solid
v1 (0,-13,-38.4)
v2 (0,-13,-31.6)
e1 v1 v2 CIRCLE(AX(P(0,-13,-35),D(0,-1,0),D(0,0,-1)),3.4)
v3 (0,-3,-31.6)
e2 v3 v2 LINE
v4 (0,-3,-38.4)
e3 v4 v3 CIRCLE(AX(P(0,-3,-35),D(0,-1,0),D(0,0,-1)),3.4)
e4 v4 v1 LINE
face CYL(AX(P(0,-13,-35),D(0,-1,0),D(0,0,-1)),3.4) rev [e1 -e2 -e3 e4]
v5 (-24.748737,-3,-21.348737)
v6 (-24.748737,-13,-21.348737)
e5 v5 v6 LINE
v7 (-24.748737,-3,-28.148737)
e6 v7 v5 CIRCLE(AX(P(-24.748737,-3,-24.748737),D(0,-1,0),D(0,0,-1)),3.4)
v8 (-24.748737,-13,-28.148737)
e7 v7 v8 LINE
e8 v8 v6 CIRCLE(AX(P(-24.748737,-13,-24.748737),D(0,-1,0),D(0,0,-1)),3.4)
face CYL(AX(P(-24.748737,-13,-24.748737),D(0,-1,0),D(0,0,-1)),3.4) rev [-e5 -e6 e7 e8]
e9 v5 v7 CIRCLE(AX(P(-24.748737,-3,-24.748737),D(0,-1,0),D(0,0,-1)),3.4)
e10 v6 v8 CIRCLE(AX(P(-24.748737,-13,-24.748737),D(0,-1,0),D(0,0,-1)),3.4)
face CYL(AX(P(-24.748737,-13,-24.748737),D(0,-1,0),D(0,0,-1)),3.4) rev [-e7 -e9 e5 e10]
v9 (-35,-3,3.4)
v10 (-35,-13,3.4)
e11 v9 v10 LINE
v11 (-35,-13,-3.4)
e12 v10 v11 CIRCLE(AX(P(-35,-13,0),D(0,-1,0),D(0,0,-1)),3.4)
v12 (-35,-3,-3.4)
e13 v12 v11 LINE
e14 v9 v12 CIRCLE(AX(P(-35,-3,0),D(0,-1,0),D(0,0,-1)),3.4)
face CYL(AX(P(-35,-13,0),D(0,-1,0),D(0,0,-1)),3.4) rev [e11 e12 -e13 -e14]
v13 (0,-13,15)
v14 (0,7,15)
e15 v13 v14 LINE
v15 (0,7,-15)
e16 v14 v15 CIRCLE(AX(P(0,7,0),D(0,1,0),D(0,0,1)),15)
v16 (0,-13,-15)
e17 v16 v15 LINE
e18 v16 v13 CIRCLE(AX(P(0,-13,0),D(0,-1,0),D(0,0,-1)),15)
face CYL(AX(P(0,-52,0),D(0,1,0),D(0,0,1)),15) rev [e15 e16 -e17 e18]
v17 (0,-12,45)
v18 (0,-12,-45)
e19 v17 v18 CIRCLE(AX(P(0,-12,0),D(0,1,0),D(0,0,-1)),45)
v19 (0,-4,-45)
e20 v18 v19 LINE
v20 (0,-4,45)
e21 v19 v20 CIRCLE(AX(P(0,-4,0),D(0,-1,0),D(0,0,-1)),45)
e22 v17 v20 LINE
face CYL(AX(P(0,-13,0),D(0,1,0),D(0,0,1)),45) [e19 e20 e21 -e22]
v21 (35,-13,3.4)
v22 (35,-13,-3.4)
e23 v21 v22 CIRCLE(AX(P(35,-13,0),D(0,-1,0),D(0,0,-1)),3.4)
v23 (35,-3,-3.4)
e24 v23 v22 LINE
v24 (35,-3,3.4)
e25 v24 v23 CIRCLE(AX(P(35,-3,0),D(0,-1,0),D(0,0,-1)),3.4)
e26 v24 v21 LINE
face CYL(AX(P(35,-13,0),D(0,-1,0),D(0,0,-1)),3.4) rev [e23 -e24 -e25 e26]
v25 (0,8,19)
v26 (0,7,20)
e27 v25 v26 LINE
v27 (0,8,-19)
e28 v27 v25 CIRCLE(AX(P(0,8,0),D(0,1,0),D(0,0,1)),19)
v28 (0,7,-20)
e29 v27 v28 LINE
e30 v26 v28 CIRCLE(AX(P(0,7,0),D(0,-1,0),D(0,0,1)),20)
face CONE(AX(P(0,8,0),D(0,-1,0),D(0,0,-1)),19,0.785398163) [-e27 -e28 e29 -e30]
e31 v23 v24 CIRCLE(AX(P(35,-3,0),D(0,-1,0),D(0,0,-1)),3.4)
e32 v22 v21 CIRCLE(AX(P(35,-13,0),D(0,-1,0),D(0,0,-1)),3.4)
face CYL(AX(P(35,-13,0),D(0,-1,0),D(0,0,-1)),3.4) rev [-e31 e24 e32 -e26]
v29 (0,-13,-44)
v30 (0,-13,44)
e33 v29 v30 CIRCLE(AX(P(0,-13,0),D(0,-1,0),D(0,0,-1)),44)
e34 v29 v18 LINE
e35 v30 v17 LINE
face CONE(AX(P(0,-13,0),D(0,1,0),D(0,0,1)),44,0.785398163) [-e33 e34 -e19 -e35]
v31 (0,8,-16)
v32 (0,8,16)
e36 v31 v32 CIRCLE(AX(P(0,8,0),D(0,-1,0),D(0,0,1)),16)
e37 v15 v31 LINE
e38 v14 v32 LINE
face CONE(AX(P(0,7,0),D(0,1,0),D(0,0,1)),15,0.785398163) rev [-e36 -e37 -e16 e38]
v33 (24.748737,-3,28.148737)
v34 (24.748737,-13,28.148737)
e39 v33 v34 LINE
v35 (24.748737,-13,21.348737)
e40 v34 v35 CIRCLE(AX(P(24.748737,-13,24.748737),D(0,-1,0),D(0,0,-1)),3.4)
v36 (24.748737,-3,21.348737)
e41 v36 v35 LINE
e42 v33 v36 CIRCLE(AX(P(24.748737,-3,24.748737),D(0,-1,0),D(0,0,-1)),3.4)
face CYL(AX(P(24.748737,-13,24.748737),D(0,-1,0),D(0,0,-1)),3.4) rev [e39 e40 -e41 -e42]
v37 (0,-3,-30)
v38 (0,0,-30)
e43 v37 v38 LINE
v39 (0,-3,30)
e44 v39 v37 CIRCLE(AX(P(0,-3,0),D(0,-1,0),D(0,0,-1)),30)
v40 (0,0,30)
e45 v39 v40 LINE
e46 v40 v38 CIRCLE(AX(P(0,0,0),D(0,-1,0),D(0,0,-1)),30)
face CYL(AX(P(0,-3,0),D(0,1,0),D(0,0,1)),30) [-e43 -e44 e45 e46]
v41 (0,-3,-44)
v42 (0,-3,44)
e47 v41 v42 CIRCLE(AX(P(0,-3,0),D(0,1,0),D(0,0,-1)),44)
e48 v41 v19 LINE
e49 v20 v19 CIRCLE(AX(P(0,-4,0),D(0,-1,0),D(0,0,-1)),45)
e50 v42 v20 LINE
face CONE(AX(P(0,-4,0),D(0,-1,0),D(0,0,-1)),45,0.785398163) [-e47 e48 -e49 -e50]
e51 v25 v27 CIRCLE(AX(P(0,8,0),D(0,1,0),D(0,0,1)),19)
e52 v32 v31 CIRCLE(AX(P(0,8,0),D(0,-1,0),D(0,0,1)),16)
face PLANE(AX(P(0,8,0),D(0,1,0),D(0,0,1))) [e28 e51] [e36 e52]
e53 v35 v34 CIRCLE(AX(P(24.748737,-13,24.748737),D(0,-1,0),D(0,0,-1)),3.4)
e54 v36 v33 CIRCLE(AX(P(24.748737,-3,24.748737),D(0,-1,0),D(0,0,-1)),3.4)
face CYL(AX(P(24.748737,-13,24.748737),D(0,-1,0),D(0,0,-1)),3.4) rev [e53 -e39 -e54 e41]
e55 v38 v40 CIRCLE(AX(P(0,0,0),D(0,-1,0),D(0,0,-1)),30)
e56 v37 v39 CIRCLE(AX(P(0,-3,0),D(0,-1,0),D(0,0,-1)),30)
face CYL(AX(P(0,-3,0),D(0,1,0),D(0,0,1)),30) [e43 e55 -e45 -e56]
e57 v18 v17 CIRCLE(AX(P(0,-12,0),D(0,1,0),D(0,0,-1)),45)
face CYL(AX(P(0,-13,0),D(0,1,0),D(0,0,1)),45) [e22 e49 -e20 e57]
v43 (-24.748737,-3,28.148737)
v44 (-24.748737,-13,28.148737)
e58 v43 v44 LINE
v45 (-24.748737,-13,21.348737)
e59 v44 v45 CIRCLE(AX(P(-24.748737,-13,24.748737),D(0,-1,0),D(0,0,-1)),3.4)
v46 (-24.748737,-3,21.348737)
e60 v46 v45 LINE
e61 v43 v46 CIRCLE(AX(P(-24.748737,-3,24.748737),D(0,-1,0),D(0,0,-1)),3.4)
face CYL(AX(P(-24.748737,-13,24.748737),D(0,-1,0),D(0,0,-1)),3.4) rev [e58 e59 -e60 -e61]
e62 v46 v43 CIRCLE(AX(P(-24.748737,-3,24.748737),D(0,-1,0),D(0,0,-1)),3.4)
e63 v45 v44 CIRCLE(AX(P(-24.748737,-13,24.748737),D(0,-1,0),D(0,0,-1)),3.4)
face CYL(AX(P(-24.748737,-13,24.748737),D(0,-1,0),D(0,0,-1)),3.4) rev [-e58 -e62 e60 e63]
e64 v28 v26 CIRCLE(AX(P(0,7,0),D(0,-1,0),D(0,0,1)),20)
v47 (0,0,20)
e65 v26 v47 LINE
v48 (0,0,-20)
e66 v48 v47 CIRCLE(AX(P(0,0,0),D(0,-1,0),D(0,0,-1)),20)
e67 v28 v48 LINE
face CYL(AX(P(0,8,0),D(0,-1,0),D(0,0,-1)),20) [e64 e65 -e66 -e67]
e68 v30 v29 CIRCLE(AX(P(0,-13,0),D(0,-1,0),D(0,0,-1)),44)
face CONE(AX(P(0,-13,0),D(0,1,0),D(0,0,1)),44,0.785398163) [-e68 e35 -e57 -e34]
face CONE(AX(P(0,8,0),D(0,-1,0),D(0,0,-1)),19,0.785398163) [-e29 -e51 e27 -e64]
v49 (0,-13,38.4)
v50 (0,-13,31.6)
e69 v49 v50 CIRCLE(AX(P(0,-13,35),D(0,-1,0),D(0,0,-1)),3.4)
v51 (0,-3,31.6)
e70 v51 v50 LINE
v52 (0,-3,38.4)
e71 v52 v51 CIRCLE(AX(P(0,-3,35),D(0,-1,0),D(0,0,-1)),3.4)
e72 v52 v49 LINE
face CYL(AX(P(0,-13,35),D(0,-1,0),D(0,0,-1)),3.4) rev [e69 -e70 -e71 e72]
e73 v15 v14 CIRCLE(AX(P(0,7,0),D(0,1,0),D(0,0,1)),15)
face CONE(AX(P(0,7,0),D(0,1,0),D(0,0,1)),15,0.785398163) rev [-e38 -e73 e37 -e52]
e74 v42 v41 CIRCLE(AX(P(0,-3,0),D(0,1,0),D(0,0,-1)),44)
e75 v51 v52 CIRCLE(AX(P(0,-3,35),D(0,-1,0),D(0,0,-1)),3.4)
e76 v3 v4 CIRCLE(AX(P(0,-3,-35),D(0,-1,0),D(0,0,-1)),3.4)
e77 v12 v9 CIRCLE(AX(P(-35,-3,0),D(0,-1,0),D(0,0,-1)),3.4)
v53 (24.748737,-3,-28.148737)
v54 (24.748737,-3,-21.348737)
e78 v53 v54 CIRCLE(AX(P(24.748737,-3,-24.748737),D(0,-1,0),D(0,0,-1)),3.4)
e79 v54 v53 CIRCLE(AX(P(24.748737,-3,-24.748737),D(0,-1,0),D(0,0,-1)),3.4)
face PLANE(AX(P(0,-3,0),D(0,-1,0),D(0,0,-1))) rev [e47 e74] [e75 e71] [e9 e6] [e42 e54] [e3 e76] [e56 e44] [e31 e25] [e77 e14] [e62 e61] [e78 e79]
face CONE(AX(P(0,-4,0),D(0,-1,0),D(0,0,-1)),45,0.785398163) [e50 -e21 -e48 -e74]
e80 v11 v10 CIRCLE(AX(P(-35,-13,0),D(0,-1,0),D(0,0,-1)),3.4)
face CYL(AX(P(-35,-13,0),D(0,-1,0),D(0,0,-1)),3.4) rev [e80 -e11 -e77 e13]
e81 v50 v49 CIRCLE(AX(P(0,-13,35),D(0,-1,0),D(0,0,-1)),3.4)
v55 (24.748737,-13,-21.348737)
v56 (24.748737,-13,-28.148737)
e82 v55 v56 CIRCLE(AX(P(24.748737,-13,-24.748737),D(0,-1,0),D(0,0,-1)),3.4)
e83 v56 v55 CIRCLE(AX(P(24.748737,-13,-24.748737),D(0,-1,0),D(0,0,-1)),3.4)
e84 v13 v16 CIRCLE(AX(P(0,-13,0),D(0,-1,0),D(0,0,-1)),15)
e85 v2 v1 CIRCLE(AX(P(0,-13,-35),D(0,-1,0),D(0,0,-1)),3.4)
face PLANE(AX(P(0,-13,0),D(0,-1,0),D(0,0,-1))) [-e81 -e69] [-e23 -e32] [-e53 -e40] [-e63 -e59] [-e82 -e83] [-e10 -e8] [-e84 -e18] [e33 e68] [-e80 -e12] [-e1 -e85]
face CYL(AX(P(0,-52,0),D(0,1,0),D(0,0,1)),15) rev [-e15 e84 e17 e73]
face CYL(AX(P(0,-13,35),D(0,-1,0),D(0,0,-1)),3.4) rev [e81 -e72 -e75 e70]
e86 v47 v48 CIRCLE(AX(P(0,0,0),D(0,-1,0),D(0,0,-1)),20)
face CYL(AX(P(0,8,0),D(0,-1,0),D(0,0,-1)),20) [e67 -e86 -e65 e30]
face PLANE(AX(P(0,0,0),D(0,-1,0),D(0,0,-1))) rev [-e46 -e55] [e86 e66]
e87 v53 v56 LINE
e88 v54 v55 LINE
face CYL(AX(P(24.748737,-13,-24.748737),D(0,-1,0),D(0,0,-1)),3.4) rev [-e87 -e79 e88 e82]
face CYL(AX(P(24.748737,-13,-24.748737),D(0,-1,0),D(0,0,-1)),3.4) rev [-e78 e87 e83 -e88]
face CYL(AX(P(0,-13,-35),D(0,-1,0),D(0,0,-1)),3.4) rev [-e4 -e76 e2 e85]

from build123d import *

# Parameters (mm, degrees)
SKETCH1_R           = 20
BOSS_EXTRUDE1_DEPTH = 8
SKETCH3_R           = 30
BOSS_EXTRUDE2_DEPTH = 3
SKETCH4_R           = 45
BOSS_EXTRUDE3_DEPTH = 10
SKETCH5_R           = 15
CUT_EXTRUDE1_DEPTH  = 60
M8_TAPPED_HOLE1_D   = 6.8
CIRPATTERN2_COUNT   = 8
CHAMFER1_SIZE       = 1
CHAMFER2_SIZE       = 1


with BuildPart() as part:
    # Sketch1 → Boss-Extrude1 (new body)
    with BuildSketch(Plane(origin=(0, 0, 0), x_dir=(1, 0, 0), z_dir=(0, 1, 0))):
        with Locations(Location((0, 0, 0), (0, 0, 270))):
            Circle(SKETCH1_R)
    extrude(amount=BOSS_EXTRUDE1_DEPTH)

    # Sketch3 → Boss-Extrude2 (add)
    with BuildSketch(Plane.XZ):
        with Locations(Location((0, 0, 0), (0, 0, 270))):
            Circle(SKETCH3_R)
    extrude(amount=BOSS_EXTRUDE2_DEPTH)

    # Sketch4 → Boss-Extrude3 (add)
    with BuildSketch(Plane.XZ.offset(3)):
        with Locations(Location((0, 0, 0), (0, 0, 270))):
            Circle(SKETCH4_R)
    extrude(amount=BOSS_EXTRUDE3_DEPTH)

    # Sketch5 → Cut-Extrude1 (cut)
    with BuildSketch(Plane(origin=(0, 8, 0), x_dir=(1, 0, 0), z_dir=(0, 1, 0))):
        with Locations(Location((0, 0, 0), (0, 0, 270))):
            Circle(SKETCH5_R)
    extrude(amount=-CUT_EXTRUDE1_DEPTH, mode=Mode.SUBTRACT)

    # M8 Tapped Hole1 (through all)
    with Locations(Plane(origin=(0, -13, 0), x_dir=(-1, 0, 0), z_dir=(0, -1, 0))):
        with Locations((0, -35)):
            m8_tapped_hole1 = Hole(M8_TAPPED_HOLE1_D / 2)

    # CirPattern2: M8 Tapped Hole1 ×8 about axis
    cirpattern2_axis = Axis((0, 0, 0), (0, 1, 0))
    for i in range(1, CIRPATTERN2_COUNT):
        add(m8_tapped_hole1.rotate(cirpattern2_axis, i * 360 / CIRPATTERN2_COUNT), mode=Mode.SUBTRACT)

    # Chamfer1
    chamfer1_edges = [part.edges().sort_by_distance(p)[0] for p in [
        (0, -13, 45),
        (0, -3, 45),
    ]]
    chamfer(chamfer1_edges, length=CHAMFER1_SIZE)

    # Chamfer2
    chamfer2_edges = [part.edges().sort_by_distance(p)[0] for p in [
        (0, 8, -15),
        (0, 8, -20),
    ]]
    chamfer(chamfer2_edges, length=CHAMFER2_SIZE)


solid = part.part
